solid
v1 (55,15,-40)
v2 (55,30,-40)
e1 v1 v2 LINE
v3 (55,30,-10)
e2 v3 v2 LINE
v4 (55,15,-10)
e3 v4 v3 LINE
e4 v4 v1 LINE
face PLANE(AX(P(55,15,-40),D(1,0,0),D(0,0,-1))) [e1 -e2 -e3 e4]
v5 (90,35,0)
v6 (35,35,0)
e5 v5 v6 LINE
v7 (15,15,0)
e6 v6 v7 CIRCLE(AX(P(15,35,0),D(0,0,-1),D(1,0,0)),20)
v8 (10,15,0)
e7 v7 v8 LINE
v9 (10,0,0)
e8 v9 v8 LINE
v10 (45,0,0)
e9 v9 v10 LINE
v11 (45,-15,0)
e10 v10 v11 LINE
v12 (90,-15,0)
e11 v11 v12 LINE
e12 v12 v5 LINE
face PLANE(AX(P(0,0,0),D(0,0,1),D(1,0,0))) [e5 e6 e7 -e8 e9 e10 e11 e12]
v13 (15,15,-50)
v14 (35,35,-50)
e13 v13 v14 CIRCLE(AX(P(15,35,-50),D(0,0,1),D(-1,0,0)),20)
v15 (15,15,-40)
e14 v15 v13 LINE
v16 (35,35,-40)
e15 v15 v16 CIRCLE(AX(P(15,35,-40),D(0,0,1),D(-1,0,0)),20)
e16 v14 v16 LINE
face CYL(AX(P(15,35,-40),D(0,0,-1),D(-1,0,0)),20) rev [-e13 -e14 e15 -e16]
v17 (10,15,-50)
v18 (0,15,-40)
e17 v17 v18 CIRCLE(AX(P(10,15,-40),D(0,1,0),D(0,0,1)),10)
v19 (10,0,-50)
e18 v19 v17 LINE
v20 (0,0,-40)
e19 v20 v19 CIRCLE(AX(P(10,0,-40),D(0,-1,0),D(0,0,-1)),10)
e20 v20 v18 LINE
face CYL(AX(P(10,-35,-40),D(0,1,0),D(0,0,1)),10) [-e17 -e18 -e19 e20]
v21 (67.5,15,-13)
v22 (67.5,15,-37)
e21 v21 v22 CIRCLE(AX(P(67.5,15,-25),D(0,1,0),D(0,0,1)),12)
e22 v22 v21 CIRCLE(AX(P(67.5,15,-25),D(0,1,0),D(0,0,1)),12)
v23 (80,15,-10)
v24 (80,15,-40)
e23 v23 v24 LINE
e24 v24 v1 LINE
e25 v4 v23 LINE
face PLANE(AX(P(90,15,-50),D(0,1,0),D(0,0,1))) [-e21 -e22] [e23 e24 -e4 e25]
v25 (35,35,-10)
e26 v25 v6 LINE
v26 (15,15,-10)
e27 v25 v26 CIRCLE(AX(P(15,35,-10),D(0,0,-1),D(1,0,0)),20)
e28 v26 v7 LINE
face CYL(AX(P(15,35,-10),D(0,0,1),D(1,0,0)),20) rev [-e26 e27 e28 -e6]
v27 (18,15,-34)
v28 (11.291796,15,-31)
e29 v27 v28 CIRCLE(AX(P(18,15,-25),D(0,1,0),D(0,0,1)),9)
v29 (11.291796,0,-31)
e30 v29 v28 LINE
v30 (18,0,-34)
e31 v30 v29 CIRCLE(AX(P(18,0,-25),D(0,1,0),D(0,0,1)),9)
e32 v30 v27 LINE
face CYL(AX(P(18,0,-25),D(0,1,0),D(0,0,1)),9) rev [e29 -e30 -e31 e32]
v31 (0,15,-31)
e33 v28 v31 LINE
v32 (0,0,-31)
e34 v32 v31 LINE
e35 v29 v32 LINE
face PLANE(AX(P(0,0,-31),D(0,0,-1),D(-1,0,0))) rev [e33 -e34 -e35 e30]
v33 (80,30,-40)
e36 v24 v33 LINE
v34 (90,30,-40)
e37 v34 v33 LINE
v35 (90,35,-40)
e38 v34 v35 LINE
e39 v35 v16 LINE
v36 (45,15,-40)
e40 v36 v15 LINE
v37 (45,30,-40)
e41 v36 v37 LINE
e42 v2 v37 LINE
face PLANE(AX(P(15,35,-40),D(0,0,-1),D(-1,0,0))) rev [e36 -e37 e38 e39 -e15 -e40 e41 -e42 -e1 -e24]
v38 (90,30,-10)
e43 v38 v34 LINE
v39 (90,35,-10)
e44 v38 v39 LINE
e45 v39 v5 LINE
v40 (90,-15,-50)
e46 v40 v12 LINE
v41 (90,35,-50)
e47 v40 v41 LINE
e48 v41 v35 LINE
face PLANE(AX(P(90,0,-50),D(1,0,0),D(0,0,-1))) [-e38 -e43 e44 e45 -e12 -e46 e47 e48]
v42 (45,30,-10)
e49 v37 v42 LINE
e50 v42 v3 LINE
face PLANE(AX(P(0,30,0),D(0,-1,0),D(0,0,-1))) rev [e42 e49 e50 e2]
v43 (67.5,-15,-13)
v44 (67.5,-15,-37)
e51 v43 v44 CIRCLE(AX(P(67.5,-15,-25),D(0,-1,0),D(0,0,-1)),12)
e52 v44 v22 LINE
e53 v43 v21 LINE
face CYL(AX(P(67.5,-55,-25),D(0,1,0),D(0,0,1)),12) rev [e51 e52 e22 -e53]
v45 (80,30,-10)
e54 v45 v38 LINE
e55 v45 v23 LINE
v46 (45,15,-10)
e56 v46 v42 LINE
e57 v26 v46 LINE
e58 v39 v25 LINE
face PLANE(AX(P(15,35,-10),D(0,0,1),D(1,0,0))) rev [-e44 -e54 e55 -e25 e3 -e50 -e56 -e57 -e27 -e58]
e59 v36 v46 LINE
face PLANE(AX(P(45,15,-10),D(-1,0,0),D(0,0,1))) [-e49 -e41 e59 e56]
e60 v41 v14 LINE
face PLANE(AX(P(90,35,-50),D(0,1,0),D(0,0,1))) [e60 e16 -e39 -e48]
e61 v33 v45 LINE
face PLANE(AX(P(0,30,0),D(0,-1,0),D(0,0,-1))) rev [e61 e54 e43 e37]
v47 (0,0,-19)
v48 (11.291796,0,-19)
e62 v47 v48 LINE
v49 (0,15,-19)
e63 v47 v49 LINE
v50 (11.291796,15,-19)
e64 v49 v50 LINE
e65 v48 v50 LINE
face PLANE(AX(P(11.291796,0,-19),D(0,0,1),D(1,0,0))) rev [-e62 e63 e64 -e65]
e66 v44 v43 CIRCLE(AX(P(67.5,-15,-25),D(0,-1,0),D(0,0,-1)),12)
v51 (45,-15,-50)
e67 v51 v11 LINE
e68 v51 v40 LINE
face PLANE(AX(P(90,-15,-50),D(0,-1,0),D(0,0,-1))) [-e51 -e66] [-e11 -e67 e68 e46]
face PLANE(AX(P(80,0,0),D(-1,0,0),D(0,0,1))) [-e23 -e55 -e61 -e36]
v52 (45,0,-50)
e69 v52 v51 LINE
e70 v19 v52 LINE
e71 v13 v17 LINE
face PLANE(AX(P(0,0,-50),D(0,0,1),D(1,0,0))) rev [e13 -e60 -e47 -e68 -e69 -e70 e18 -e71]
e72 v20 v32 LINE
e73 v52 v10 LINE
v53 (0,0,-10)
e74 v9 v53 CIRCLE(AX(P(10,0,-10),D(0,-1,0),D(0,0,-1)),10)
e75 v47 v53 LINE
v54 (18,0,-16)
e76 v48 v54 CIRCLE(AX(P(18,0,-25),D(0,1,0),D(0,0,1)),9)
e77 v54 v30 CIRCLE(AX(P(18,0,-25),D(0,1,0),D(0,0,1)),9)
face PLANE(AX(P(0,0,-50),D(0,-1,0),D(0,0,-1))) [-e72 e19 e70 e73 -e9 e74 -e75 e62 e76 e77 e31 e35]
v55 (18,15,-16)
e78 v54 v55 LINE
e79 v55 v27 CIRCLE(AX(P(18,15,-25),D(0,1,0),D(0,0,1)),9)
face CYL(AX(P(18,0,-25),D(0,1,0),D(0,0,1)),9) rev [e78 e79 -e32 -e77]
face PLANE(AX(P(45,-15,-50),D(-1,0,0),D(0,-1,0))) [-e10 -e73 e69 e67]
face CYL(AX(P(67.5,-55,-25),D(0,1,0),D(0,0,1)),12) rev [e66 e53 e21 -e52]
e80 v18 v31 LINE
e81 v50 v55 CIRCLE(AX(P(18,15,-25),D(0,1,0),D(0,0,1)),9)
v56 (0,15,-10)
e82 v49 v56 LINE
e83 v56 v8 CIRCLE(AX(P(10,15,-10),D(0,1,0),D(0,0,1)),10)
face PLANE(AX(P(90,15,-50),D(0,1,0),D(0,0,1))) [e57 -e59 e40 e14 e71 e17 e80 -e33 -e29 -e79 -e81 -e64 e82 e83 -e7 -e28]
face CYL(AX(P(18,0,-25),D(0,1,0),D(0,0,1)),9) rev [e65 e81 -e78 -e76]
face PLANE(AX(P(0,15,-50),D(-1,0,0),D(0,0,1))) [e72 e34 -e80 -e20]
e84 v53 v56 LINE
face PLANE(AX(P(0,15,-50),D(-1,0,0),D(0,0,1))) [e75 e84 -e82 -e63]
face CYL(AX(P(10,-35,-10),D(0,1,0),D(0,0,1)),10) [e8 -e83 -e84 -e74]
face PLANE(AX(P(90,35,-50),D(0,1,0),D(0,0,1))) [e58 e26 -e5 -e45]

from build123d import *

# Parameters (mm, degrees)
BASE_PLATE_SKETCH_W      = 90
BASE_PLATE_SKETCH_H      = 15
BASE_PLATE_DEPTH         = 50
SIDE_WALL_SKETCH_W       = 45
SIDE_WALL_SKETCH_H       = 15
SIDE_WALL_DEPTH          = 50
RAISED_BLOCK_SKETCH_W    = 55
RAISED_BLOCK_SKETCH_H    = 20
RAISED_BLOCK_DEPTH       = 50
STEP_NOTCH_CUT_DEPTH     = 50
FIRST_ROUNDED_LUG_DEPTH  = 10
SECOND_START             = -10
SECOND_ROUNDED_LUG_DEPTH = 10
SLOT_CUT_DEPTH           = 15
CHANNEL_SKETCH_W         = 30
CHANNEL_SKETCH_H         = 20
CHANNEL_CUT_DEPTH        = 60
RAIL_BOSS_SKETCH_W       = 30
RAIL_BOSS_SKETCH_H       = 20
RAIL_BOSS_DEPTH          = 10
CURVED_RECESS_SKETCH_W   = 10
CURVED_RECESS_SKETCH_H   = 30
CURVED_RECESS_CUT_DEPTH  = 5
BRIDGE_BLOCK_SKETCH_W    = 10
BRIDGE_BLOCK_SKETCH_H    = 30
BRIDGE_BLOCK_DEPTH       = 20
BRIDGE_RELIEF_SKETCH_W   = 10
BRIDGE_RELIEF_SKETCH_H   = 30
BRIDGE_RELIEF_CUT_DEPTH  = 5
BORE_24_SKETCH_R         = 12
BORE_24_DEPTH            = 70


with BuildPart() as part:
    # Base Plate Sketch → Base Plate (new body)
    with BuildSketch(Plane.XY):
        with Locations((45, 7.5)):
            Rectangle(BASE_PLATE_SKETCH_W, BASE_PLATE_SKETCH_H)
    extrude(amount=-BASE_PLATE_DEPTH)

    # Side Wall Sketch → Side Wall (add)
    with BuildSketch(Plane.XY):
        with Locations((67.5, -7.5)):
            Rectangle(SIDE_WALL_SKETCH_W, SIDE_WALL_SKETCH_H)
    extrude(amount=-SIDE_WALL_DEPTH)

    # Raised Block Sketch → Raised Block (add)
    with BuildSketch(Plane.XY):
        with Locations((62.5, 25)):
            Rectangle(RAISED_BLOCK_SKETCH_W, RAISED_BLOCK_SKETCH_H)
    extrude(amount=-RAISED_BLOCK_DEPTH)

    # Step Notch Sketch → Step Notch Cut (cut)
    with BuildSketch(Plane(origin=(0, 15, 0), x_dir=(1, 0, 0), z_dir=(0, 1, 0))):
        with BuildLine():
            Line((10, 50), (0, 50))
            Line((0, 50), (0, 40))
            ThreePointArc((0, 40), (2.928932188, 47.071067812), (10, 50))
        make_face()
        with BuildLine():
            ThreePointArc((10, 0), (2.928932188, 2.928932188), (0, 10))
            Line((0, 10), (0, 0))
            Line((0, 0), (10, 0))
        make_face()
    extrude(amount=-STEP_NOTCH_CUT_DEPTH, mode=Mode.SUBTRACT)

    # First Rounded Lug Sketch → First Rounded Lug (add)
    with BuildSketch(Plane.XY):
        with BuildLine():
            Line((35, 35), (35, 15))
            Line((35, 15), (15, 15))
            ThreePointArc((15, 15), (29.142135624, 20.857864376), (35, 35))
        make_face()
    extrude(amount=-FIRST_ROUNDED_LUG_DEPTH)

    # Second Rounded Lug Sketch → Second Rounded Lug (add)
    with BuildSketch(Plane(origin=(0, 0, -50), x_dir=(-1, 0, 0), z_dir=(0, 0, -1)).offset(SECOND_START)):
        with BuildLine():
            Line((-35, 35), (-35, 15))
            Line((-35, 15), (-15, 15))
            ThreePointArc((-15, 15), (-29.142135624, 20.857864376), (-35, 35))
        make_face()
    extrude(amount=SECOND_ROUNDED_LUG_DEPTH)

    # Slot Sketch → Slot Cut (cut)
    with BuildSketch(Plane(origin=(0, 15, 0), x_dir=(1, 0, 0), z_dir=(0, 1, 0))):
        with BuildLine():
            Line((0, 25), (0, 31))
            Line((0, 31), (11.291796068, 31))
            ThreePointArc((11.291796068, 31), (27, 25), (11.291796068, 19))
            Line((11.291796068, 19), (0, 19))
            Line((0, 19), (0, 25))
        make_face()
    extrude(amount=-SLOT_CUT_DEPTH, mode=Mode.SUBTRACT)

    # Channel Sketch → Channel Cut (cut)
    with BuildSketch(Plane.ZY.offset(-35)):
        with Locations((-25, 25)):
            Rectangle(CHANNEL_SKETCH_W, CHANNEL_SKETCH_H)
    extrude(amount=-CHANNEL_CUT_DEPTH, mode=Mode.SUBTRACT)

    # Rail Boss Sketch → Rail Boss (add)
    with BuildSketch(Plane(origin=(90, 0, 0), x_dir=(0, 0, -1), z_dir=(1, 0, 0))):
        with Locations((25, 25)):
            Rectangle(RAIL_BOSS_SKETCH_W, RAIL_BOSS_SKETCH_H)
    extrude(amount=-RAIL_BOSS_DEPTH)

    # Curved Recess Sketch → Curved Recess Cut (cut)
    with BuildSketch(Plane(origin=(0, 35, 0), x_dir=(1, 0, 0), z_dir=(0, 1, 0))):
        with Locations((85, 25)):
            Rectangle(CURVED_RECESS_SKETCH_W, CURVED_RECESS_SKETCH_H)
    extrude(amount=-CURVED_RECESS_CUT_DEPTH, mode=Mode.SUBTRACT)

    # Bridge Block Sketch → Bridge Block (add)
    with BuildSketch(Plane(origin=(0, 35, 0), x_dir=(1, 0, 0), z_dir=(0, 1, 0))):
        with Locations((50, 25)):
            Rectangle(BRIDGE_BLOCK_SKETCH_W, BRIDGE_BLOCK_SKETCH_H)
    extrude(amount=-BRIDGE_BLOCK_DEPTH)

    # Bridge Relief Sketch → Bridge Relief Cut (cut)
    with BuildSketch(Plane(origin=(0, 35, 0), x_dir=(1, 0, 0), z_dir=(0, 1, 0))):
        with Locations((50, 25)):
            Rectangle(BRIDGE_RELIEF_SKETCH_W, BRIDGE_RELIEF_SKETCH_H)
    extrude(amount=-BRIDGE_RELIEF_CUT_DEPTH, mode=Mode.SUBTRACT)

    # Bore Ø24 Sketch → Bore Ø24 (cut)
    with BuildSketch(Plane(origin=(0, 15, 0), x_dir=(1, 0, 0), z_dir=(0, 1, 0))):
        with Locations(Location((67.5, 25, 0), (0, 0, 270))):
            Circle(BORE_24_SKETCH_R)
    extrude(amount=-BORE_24_DEPTH, mode=Mode.SUBTRACT)


solid = part.part
